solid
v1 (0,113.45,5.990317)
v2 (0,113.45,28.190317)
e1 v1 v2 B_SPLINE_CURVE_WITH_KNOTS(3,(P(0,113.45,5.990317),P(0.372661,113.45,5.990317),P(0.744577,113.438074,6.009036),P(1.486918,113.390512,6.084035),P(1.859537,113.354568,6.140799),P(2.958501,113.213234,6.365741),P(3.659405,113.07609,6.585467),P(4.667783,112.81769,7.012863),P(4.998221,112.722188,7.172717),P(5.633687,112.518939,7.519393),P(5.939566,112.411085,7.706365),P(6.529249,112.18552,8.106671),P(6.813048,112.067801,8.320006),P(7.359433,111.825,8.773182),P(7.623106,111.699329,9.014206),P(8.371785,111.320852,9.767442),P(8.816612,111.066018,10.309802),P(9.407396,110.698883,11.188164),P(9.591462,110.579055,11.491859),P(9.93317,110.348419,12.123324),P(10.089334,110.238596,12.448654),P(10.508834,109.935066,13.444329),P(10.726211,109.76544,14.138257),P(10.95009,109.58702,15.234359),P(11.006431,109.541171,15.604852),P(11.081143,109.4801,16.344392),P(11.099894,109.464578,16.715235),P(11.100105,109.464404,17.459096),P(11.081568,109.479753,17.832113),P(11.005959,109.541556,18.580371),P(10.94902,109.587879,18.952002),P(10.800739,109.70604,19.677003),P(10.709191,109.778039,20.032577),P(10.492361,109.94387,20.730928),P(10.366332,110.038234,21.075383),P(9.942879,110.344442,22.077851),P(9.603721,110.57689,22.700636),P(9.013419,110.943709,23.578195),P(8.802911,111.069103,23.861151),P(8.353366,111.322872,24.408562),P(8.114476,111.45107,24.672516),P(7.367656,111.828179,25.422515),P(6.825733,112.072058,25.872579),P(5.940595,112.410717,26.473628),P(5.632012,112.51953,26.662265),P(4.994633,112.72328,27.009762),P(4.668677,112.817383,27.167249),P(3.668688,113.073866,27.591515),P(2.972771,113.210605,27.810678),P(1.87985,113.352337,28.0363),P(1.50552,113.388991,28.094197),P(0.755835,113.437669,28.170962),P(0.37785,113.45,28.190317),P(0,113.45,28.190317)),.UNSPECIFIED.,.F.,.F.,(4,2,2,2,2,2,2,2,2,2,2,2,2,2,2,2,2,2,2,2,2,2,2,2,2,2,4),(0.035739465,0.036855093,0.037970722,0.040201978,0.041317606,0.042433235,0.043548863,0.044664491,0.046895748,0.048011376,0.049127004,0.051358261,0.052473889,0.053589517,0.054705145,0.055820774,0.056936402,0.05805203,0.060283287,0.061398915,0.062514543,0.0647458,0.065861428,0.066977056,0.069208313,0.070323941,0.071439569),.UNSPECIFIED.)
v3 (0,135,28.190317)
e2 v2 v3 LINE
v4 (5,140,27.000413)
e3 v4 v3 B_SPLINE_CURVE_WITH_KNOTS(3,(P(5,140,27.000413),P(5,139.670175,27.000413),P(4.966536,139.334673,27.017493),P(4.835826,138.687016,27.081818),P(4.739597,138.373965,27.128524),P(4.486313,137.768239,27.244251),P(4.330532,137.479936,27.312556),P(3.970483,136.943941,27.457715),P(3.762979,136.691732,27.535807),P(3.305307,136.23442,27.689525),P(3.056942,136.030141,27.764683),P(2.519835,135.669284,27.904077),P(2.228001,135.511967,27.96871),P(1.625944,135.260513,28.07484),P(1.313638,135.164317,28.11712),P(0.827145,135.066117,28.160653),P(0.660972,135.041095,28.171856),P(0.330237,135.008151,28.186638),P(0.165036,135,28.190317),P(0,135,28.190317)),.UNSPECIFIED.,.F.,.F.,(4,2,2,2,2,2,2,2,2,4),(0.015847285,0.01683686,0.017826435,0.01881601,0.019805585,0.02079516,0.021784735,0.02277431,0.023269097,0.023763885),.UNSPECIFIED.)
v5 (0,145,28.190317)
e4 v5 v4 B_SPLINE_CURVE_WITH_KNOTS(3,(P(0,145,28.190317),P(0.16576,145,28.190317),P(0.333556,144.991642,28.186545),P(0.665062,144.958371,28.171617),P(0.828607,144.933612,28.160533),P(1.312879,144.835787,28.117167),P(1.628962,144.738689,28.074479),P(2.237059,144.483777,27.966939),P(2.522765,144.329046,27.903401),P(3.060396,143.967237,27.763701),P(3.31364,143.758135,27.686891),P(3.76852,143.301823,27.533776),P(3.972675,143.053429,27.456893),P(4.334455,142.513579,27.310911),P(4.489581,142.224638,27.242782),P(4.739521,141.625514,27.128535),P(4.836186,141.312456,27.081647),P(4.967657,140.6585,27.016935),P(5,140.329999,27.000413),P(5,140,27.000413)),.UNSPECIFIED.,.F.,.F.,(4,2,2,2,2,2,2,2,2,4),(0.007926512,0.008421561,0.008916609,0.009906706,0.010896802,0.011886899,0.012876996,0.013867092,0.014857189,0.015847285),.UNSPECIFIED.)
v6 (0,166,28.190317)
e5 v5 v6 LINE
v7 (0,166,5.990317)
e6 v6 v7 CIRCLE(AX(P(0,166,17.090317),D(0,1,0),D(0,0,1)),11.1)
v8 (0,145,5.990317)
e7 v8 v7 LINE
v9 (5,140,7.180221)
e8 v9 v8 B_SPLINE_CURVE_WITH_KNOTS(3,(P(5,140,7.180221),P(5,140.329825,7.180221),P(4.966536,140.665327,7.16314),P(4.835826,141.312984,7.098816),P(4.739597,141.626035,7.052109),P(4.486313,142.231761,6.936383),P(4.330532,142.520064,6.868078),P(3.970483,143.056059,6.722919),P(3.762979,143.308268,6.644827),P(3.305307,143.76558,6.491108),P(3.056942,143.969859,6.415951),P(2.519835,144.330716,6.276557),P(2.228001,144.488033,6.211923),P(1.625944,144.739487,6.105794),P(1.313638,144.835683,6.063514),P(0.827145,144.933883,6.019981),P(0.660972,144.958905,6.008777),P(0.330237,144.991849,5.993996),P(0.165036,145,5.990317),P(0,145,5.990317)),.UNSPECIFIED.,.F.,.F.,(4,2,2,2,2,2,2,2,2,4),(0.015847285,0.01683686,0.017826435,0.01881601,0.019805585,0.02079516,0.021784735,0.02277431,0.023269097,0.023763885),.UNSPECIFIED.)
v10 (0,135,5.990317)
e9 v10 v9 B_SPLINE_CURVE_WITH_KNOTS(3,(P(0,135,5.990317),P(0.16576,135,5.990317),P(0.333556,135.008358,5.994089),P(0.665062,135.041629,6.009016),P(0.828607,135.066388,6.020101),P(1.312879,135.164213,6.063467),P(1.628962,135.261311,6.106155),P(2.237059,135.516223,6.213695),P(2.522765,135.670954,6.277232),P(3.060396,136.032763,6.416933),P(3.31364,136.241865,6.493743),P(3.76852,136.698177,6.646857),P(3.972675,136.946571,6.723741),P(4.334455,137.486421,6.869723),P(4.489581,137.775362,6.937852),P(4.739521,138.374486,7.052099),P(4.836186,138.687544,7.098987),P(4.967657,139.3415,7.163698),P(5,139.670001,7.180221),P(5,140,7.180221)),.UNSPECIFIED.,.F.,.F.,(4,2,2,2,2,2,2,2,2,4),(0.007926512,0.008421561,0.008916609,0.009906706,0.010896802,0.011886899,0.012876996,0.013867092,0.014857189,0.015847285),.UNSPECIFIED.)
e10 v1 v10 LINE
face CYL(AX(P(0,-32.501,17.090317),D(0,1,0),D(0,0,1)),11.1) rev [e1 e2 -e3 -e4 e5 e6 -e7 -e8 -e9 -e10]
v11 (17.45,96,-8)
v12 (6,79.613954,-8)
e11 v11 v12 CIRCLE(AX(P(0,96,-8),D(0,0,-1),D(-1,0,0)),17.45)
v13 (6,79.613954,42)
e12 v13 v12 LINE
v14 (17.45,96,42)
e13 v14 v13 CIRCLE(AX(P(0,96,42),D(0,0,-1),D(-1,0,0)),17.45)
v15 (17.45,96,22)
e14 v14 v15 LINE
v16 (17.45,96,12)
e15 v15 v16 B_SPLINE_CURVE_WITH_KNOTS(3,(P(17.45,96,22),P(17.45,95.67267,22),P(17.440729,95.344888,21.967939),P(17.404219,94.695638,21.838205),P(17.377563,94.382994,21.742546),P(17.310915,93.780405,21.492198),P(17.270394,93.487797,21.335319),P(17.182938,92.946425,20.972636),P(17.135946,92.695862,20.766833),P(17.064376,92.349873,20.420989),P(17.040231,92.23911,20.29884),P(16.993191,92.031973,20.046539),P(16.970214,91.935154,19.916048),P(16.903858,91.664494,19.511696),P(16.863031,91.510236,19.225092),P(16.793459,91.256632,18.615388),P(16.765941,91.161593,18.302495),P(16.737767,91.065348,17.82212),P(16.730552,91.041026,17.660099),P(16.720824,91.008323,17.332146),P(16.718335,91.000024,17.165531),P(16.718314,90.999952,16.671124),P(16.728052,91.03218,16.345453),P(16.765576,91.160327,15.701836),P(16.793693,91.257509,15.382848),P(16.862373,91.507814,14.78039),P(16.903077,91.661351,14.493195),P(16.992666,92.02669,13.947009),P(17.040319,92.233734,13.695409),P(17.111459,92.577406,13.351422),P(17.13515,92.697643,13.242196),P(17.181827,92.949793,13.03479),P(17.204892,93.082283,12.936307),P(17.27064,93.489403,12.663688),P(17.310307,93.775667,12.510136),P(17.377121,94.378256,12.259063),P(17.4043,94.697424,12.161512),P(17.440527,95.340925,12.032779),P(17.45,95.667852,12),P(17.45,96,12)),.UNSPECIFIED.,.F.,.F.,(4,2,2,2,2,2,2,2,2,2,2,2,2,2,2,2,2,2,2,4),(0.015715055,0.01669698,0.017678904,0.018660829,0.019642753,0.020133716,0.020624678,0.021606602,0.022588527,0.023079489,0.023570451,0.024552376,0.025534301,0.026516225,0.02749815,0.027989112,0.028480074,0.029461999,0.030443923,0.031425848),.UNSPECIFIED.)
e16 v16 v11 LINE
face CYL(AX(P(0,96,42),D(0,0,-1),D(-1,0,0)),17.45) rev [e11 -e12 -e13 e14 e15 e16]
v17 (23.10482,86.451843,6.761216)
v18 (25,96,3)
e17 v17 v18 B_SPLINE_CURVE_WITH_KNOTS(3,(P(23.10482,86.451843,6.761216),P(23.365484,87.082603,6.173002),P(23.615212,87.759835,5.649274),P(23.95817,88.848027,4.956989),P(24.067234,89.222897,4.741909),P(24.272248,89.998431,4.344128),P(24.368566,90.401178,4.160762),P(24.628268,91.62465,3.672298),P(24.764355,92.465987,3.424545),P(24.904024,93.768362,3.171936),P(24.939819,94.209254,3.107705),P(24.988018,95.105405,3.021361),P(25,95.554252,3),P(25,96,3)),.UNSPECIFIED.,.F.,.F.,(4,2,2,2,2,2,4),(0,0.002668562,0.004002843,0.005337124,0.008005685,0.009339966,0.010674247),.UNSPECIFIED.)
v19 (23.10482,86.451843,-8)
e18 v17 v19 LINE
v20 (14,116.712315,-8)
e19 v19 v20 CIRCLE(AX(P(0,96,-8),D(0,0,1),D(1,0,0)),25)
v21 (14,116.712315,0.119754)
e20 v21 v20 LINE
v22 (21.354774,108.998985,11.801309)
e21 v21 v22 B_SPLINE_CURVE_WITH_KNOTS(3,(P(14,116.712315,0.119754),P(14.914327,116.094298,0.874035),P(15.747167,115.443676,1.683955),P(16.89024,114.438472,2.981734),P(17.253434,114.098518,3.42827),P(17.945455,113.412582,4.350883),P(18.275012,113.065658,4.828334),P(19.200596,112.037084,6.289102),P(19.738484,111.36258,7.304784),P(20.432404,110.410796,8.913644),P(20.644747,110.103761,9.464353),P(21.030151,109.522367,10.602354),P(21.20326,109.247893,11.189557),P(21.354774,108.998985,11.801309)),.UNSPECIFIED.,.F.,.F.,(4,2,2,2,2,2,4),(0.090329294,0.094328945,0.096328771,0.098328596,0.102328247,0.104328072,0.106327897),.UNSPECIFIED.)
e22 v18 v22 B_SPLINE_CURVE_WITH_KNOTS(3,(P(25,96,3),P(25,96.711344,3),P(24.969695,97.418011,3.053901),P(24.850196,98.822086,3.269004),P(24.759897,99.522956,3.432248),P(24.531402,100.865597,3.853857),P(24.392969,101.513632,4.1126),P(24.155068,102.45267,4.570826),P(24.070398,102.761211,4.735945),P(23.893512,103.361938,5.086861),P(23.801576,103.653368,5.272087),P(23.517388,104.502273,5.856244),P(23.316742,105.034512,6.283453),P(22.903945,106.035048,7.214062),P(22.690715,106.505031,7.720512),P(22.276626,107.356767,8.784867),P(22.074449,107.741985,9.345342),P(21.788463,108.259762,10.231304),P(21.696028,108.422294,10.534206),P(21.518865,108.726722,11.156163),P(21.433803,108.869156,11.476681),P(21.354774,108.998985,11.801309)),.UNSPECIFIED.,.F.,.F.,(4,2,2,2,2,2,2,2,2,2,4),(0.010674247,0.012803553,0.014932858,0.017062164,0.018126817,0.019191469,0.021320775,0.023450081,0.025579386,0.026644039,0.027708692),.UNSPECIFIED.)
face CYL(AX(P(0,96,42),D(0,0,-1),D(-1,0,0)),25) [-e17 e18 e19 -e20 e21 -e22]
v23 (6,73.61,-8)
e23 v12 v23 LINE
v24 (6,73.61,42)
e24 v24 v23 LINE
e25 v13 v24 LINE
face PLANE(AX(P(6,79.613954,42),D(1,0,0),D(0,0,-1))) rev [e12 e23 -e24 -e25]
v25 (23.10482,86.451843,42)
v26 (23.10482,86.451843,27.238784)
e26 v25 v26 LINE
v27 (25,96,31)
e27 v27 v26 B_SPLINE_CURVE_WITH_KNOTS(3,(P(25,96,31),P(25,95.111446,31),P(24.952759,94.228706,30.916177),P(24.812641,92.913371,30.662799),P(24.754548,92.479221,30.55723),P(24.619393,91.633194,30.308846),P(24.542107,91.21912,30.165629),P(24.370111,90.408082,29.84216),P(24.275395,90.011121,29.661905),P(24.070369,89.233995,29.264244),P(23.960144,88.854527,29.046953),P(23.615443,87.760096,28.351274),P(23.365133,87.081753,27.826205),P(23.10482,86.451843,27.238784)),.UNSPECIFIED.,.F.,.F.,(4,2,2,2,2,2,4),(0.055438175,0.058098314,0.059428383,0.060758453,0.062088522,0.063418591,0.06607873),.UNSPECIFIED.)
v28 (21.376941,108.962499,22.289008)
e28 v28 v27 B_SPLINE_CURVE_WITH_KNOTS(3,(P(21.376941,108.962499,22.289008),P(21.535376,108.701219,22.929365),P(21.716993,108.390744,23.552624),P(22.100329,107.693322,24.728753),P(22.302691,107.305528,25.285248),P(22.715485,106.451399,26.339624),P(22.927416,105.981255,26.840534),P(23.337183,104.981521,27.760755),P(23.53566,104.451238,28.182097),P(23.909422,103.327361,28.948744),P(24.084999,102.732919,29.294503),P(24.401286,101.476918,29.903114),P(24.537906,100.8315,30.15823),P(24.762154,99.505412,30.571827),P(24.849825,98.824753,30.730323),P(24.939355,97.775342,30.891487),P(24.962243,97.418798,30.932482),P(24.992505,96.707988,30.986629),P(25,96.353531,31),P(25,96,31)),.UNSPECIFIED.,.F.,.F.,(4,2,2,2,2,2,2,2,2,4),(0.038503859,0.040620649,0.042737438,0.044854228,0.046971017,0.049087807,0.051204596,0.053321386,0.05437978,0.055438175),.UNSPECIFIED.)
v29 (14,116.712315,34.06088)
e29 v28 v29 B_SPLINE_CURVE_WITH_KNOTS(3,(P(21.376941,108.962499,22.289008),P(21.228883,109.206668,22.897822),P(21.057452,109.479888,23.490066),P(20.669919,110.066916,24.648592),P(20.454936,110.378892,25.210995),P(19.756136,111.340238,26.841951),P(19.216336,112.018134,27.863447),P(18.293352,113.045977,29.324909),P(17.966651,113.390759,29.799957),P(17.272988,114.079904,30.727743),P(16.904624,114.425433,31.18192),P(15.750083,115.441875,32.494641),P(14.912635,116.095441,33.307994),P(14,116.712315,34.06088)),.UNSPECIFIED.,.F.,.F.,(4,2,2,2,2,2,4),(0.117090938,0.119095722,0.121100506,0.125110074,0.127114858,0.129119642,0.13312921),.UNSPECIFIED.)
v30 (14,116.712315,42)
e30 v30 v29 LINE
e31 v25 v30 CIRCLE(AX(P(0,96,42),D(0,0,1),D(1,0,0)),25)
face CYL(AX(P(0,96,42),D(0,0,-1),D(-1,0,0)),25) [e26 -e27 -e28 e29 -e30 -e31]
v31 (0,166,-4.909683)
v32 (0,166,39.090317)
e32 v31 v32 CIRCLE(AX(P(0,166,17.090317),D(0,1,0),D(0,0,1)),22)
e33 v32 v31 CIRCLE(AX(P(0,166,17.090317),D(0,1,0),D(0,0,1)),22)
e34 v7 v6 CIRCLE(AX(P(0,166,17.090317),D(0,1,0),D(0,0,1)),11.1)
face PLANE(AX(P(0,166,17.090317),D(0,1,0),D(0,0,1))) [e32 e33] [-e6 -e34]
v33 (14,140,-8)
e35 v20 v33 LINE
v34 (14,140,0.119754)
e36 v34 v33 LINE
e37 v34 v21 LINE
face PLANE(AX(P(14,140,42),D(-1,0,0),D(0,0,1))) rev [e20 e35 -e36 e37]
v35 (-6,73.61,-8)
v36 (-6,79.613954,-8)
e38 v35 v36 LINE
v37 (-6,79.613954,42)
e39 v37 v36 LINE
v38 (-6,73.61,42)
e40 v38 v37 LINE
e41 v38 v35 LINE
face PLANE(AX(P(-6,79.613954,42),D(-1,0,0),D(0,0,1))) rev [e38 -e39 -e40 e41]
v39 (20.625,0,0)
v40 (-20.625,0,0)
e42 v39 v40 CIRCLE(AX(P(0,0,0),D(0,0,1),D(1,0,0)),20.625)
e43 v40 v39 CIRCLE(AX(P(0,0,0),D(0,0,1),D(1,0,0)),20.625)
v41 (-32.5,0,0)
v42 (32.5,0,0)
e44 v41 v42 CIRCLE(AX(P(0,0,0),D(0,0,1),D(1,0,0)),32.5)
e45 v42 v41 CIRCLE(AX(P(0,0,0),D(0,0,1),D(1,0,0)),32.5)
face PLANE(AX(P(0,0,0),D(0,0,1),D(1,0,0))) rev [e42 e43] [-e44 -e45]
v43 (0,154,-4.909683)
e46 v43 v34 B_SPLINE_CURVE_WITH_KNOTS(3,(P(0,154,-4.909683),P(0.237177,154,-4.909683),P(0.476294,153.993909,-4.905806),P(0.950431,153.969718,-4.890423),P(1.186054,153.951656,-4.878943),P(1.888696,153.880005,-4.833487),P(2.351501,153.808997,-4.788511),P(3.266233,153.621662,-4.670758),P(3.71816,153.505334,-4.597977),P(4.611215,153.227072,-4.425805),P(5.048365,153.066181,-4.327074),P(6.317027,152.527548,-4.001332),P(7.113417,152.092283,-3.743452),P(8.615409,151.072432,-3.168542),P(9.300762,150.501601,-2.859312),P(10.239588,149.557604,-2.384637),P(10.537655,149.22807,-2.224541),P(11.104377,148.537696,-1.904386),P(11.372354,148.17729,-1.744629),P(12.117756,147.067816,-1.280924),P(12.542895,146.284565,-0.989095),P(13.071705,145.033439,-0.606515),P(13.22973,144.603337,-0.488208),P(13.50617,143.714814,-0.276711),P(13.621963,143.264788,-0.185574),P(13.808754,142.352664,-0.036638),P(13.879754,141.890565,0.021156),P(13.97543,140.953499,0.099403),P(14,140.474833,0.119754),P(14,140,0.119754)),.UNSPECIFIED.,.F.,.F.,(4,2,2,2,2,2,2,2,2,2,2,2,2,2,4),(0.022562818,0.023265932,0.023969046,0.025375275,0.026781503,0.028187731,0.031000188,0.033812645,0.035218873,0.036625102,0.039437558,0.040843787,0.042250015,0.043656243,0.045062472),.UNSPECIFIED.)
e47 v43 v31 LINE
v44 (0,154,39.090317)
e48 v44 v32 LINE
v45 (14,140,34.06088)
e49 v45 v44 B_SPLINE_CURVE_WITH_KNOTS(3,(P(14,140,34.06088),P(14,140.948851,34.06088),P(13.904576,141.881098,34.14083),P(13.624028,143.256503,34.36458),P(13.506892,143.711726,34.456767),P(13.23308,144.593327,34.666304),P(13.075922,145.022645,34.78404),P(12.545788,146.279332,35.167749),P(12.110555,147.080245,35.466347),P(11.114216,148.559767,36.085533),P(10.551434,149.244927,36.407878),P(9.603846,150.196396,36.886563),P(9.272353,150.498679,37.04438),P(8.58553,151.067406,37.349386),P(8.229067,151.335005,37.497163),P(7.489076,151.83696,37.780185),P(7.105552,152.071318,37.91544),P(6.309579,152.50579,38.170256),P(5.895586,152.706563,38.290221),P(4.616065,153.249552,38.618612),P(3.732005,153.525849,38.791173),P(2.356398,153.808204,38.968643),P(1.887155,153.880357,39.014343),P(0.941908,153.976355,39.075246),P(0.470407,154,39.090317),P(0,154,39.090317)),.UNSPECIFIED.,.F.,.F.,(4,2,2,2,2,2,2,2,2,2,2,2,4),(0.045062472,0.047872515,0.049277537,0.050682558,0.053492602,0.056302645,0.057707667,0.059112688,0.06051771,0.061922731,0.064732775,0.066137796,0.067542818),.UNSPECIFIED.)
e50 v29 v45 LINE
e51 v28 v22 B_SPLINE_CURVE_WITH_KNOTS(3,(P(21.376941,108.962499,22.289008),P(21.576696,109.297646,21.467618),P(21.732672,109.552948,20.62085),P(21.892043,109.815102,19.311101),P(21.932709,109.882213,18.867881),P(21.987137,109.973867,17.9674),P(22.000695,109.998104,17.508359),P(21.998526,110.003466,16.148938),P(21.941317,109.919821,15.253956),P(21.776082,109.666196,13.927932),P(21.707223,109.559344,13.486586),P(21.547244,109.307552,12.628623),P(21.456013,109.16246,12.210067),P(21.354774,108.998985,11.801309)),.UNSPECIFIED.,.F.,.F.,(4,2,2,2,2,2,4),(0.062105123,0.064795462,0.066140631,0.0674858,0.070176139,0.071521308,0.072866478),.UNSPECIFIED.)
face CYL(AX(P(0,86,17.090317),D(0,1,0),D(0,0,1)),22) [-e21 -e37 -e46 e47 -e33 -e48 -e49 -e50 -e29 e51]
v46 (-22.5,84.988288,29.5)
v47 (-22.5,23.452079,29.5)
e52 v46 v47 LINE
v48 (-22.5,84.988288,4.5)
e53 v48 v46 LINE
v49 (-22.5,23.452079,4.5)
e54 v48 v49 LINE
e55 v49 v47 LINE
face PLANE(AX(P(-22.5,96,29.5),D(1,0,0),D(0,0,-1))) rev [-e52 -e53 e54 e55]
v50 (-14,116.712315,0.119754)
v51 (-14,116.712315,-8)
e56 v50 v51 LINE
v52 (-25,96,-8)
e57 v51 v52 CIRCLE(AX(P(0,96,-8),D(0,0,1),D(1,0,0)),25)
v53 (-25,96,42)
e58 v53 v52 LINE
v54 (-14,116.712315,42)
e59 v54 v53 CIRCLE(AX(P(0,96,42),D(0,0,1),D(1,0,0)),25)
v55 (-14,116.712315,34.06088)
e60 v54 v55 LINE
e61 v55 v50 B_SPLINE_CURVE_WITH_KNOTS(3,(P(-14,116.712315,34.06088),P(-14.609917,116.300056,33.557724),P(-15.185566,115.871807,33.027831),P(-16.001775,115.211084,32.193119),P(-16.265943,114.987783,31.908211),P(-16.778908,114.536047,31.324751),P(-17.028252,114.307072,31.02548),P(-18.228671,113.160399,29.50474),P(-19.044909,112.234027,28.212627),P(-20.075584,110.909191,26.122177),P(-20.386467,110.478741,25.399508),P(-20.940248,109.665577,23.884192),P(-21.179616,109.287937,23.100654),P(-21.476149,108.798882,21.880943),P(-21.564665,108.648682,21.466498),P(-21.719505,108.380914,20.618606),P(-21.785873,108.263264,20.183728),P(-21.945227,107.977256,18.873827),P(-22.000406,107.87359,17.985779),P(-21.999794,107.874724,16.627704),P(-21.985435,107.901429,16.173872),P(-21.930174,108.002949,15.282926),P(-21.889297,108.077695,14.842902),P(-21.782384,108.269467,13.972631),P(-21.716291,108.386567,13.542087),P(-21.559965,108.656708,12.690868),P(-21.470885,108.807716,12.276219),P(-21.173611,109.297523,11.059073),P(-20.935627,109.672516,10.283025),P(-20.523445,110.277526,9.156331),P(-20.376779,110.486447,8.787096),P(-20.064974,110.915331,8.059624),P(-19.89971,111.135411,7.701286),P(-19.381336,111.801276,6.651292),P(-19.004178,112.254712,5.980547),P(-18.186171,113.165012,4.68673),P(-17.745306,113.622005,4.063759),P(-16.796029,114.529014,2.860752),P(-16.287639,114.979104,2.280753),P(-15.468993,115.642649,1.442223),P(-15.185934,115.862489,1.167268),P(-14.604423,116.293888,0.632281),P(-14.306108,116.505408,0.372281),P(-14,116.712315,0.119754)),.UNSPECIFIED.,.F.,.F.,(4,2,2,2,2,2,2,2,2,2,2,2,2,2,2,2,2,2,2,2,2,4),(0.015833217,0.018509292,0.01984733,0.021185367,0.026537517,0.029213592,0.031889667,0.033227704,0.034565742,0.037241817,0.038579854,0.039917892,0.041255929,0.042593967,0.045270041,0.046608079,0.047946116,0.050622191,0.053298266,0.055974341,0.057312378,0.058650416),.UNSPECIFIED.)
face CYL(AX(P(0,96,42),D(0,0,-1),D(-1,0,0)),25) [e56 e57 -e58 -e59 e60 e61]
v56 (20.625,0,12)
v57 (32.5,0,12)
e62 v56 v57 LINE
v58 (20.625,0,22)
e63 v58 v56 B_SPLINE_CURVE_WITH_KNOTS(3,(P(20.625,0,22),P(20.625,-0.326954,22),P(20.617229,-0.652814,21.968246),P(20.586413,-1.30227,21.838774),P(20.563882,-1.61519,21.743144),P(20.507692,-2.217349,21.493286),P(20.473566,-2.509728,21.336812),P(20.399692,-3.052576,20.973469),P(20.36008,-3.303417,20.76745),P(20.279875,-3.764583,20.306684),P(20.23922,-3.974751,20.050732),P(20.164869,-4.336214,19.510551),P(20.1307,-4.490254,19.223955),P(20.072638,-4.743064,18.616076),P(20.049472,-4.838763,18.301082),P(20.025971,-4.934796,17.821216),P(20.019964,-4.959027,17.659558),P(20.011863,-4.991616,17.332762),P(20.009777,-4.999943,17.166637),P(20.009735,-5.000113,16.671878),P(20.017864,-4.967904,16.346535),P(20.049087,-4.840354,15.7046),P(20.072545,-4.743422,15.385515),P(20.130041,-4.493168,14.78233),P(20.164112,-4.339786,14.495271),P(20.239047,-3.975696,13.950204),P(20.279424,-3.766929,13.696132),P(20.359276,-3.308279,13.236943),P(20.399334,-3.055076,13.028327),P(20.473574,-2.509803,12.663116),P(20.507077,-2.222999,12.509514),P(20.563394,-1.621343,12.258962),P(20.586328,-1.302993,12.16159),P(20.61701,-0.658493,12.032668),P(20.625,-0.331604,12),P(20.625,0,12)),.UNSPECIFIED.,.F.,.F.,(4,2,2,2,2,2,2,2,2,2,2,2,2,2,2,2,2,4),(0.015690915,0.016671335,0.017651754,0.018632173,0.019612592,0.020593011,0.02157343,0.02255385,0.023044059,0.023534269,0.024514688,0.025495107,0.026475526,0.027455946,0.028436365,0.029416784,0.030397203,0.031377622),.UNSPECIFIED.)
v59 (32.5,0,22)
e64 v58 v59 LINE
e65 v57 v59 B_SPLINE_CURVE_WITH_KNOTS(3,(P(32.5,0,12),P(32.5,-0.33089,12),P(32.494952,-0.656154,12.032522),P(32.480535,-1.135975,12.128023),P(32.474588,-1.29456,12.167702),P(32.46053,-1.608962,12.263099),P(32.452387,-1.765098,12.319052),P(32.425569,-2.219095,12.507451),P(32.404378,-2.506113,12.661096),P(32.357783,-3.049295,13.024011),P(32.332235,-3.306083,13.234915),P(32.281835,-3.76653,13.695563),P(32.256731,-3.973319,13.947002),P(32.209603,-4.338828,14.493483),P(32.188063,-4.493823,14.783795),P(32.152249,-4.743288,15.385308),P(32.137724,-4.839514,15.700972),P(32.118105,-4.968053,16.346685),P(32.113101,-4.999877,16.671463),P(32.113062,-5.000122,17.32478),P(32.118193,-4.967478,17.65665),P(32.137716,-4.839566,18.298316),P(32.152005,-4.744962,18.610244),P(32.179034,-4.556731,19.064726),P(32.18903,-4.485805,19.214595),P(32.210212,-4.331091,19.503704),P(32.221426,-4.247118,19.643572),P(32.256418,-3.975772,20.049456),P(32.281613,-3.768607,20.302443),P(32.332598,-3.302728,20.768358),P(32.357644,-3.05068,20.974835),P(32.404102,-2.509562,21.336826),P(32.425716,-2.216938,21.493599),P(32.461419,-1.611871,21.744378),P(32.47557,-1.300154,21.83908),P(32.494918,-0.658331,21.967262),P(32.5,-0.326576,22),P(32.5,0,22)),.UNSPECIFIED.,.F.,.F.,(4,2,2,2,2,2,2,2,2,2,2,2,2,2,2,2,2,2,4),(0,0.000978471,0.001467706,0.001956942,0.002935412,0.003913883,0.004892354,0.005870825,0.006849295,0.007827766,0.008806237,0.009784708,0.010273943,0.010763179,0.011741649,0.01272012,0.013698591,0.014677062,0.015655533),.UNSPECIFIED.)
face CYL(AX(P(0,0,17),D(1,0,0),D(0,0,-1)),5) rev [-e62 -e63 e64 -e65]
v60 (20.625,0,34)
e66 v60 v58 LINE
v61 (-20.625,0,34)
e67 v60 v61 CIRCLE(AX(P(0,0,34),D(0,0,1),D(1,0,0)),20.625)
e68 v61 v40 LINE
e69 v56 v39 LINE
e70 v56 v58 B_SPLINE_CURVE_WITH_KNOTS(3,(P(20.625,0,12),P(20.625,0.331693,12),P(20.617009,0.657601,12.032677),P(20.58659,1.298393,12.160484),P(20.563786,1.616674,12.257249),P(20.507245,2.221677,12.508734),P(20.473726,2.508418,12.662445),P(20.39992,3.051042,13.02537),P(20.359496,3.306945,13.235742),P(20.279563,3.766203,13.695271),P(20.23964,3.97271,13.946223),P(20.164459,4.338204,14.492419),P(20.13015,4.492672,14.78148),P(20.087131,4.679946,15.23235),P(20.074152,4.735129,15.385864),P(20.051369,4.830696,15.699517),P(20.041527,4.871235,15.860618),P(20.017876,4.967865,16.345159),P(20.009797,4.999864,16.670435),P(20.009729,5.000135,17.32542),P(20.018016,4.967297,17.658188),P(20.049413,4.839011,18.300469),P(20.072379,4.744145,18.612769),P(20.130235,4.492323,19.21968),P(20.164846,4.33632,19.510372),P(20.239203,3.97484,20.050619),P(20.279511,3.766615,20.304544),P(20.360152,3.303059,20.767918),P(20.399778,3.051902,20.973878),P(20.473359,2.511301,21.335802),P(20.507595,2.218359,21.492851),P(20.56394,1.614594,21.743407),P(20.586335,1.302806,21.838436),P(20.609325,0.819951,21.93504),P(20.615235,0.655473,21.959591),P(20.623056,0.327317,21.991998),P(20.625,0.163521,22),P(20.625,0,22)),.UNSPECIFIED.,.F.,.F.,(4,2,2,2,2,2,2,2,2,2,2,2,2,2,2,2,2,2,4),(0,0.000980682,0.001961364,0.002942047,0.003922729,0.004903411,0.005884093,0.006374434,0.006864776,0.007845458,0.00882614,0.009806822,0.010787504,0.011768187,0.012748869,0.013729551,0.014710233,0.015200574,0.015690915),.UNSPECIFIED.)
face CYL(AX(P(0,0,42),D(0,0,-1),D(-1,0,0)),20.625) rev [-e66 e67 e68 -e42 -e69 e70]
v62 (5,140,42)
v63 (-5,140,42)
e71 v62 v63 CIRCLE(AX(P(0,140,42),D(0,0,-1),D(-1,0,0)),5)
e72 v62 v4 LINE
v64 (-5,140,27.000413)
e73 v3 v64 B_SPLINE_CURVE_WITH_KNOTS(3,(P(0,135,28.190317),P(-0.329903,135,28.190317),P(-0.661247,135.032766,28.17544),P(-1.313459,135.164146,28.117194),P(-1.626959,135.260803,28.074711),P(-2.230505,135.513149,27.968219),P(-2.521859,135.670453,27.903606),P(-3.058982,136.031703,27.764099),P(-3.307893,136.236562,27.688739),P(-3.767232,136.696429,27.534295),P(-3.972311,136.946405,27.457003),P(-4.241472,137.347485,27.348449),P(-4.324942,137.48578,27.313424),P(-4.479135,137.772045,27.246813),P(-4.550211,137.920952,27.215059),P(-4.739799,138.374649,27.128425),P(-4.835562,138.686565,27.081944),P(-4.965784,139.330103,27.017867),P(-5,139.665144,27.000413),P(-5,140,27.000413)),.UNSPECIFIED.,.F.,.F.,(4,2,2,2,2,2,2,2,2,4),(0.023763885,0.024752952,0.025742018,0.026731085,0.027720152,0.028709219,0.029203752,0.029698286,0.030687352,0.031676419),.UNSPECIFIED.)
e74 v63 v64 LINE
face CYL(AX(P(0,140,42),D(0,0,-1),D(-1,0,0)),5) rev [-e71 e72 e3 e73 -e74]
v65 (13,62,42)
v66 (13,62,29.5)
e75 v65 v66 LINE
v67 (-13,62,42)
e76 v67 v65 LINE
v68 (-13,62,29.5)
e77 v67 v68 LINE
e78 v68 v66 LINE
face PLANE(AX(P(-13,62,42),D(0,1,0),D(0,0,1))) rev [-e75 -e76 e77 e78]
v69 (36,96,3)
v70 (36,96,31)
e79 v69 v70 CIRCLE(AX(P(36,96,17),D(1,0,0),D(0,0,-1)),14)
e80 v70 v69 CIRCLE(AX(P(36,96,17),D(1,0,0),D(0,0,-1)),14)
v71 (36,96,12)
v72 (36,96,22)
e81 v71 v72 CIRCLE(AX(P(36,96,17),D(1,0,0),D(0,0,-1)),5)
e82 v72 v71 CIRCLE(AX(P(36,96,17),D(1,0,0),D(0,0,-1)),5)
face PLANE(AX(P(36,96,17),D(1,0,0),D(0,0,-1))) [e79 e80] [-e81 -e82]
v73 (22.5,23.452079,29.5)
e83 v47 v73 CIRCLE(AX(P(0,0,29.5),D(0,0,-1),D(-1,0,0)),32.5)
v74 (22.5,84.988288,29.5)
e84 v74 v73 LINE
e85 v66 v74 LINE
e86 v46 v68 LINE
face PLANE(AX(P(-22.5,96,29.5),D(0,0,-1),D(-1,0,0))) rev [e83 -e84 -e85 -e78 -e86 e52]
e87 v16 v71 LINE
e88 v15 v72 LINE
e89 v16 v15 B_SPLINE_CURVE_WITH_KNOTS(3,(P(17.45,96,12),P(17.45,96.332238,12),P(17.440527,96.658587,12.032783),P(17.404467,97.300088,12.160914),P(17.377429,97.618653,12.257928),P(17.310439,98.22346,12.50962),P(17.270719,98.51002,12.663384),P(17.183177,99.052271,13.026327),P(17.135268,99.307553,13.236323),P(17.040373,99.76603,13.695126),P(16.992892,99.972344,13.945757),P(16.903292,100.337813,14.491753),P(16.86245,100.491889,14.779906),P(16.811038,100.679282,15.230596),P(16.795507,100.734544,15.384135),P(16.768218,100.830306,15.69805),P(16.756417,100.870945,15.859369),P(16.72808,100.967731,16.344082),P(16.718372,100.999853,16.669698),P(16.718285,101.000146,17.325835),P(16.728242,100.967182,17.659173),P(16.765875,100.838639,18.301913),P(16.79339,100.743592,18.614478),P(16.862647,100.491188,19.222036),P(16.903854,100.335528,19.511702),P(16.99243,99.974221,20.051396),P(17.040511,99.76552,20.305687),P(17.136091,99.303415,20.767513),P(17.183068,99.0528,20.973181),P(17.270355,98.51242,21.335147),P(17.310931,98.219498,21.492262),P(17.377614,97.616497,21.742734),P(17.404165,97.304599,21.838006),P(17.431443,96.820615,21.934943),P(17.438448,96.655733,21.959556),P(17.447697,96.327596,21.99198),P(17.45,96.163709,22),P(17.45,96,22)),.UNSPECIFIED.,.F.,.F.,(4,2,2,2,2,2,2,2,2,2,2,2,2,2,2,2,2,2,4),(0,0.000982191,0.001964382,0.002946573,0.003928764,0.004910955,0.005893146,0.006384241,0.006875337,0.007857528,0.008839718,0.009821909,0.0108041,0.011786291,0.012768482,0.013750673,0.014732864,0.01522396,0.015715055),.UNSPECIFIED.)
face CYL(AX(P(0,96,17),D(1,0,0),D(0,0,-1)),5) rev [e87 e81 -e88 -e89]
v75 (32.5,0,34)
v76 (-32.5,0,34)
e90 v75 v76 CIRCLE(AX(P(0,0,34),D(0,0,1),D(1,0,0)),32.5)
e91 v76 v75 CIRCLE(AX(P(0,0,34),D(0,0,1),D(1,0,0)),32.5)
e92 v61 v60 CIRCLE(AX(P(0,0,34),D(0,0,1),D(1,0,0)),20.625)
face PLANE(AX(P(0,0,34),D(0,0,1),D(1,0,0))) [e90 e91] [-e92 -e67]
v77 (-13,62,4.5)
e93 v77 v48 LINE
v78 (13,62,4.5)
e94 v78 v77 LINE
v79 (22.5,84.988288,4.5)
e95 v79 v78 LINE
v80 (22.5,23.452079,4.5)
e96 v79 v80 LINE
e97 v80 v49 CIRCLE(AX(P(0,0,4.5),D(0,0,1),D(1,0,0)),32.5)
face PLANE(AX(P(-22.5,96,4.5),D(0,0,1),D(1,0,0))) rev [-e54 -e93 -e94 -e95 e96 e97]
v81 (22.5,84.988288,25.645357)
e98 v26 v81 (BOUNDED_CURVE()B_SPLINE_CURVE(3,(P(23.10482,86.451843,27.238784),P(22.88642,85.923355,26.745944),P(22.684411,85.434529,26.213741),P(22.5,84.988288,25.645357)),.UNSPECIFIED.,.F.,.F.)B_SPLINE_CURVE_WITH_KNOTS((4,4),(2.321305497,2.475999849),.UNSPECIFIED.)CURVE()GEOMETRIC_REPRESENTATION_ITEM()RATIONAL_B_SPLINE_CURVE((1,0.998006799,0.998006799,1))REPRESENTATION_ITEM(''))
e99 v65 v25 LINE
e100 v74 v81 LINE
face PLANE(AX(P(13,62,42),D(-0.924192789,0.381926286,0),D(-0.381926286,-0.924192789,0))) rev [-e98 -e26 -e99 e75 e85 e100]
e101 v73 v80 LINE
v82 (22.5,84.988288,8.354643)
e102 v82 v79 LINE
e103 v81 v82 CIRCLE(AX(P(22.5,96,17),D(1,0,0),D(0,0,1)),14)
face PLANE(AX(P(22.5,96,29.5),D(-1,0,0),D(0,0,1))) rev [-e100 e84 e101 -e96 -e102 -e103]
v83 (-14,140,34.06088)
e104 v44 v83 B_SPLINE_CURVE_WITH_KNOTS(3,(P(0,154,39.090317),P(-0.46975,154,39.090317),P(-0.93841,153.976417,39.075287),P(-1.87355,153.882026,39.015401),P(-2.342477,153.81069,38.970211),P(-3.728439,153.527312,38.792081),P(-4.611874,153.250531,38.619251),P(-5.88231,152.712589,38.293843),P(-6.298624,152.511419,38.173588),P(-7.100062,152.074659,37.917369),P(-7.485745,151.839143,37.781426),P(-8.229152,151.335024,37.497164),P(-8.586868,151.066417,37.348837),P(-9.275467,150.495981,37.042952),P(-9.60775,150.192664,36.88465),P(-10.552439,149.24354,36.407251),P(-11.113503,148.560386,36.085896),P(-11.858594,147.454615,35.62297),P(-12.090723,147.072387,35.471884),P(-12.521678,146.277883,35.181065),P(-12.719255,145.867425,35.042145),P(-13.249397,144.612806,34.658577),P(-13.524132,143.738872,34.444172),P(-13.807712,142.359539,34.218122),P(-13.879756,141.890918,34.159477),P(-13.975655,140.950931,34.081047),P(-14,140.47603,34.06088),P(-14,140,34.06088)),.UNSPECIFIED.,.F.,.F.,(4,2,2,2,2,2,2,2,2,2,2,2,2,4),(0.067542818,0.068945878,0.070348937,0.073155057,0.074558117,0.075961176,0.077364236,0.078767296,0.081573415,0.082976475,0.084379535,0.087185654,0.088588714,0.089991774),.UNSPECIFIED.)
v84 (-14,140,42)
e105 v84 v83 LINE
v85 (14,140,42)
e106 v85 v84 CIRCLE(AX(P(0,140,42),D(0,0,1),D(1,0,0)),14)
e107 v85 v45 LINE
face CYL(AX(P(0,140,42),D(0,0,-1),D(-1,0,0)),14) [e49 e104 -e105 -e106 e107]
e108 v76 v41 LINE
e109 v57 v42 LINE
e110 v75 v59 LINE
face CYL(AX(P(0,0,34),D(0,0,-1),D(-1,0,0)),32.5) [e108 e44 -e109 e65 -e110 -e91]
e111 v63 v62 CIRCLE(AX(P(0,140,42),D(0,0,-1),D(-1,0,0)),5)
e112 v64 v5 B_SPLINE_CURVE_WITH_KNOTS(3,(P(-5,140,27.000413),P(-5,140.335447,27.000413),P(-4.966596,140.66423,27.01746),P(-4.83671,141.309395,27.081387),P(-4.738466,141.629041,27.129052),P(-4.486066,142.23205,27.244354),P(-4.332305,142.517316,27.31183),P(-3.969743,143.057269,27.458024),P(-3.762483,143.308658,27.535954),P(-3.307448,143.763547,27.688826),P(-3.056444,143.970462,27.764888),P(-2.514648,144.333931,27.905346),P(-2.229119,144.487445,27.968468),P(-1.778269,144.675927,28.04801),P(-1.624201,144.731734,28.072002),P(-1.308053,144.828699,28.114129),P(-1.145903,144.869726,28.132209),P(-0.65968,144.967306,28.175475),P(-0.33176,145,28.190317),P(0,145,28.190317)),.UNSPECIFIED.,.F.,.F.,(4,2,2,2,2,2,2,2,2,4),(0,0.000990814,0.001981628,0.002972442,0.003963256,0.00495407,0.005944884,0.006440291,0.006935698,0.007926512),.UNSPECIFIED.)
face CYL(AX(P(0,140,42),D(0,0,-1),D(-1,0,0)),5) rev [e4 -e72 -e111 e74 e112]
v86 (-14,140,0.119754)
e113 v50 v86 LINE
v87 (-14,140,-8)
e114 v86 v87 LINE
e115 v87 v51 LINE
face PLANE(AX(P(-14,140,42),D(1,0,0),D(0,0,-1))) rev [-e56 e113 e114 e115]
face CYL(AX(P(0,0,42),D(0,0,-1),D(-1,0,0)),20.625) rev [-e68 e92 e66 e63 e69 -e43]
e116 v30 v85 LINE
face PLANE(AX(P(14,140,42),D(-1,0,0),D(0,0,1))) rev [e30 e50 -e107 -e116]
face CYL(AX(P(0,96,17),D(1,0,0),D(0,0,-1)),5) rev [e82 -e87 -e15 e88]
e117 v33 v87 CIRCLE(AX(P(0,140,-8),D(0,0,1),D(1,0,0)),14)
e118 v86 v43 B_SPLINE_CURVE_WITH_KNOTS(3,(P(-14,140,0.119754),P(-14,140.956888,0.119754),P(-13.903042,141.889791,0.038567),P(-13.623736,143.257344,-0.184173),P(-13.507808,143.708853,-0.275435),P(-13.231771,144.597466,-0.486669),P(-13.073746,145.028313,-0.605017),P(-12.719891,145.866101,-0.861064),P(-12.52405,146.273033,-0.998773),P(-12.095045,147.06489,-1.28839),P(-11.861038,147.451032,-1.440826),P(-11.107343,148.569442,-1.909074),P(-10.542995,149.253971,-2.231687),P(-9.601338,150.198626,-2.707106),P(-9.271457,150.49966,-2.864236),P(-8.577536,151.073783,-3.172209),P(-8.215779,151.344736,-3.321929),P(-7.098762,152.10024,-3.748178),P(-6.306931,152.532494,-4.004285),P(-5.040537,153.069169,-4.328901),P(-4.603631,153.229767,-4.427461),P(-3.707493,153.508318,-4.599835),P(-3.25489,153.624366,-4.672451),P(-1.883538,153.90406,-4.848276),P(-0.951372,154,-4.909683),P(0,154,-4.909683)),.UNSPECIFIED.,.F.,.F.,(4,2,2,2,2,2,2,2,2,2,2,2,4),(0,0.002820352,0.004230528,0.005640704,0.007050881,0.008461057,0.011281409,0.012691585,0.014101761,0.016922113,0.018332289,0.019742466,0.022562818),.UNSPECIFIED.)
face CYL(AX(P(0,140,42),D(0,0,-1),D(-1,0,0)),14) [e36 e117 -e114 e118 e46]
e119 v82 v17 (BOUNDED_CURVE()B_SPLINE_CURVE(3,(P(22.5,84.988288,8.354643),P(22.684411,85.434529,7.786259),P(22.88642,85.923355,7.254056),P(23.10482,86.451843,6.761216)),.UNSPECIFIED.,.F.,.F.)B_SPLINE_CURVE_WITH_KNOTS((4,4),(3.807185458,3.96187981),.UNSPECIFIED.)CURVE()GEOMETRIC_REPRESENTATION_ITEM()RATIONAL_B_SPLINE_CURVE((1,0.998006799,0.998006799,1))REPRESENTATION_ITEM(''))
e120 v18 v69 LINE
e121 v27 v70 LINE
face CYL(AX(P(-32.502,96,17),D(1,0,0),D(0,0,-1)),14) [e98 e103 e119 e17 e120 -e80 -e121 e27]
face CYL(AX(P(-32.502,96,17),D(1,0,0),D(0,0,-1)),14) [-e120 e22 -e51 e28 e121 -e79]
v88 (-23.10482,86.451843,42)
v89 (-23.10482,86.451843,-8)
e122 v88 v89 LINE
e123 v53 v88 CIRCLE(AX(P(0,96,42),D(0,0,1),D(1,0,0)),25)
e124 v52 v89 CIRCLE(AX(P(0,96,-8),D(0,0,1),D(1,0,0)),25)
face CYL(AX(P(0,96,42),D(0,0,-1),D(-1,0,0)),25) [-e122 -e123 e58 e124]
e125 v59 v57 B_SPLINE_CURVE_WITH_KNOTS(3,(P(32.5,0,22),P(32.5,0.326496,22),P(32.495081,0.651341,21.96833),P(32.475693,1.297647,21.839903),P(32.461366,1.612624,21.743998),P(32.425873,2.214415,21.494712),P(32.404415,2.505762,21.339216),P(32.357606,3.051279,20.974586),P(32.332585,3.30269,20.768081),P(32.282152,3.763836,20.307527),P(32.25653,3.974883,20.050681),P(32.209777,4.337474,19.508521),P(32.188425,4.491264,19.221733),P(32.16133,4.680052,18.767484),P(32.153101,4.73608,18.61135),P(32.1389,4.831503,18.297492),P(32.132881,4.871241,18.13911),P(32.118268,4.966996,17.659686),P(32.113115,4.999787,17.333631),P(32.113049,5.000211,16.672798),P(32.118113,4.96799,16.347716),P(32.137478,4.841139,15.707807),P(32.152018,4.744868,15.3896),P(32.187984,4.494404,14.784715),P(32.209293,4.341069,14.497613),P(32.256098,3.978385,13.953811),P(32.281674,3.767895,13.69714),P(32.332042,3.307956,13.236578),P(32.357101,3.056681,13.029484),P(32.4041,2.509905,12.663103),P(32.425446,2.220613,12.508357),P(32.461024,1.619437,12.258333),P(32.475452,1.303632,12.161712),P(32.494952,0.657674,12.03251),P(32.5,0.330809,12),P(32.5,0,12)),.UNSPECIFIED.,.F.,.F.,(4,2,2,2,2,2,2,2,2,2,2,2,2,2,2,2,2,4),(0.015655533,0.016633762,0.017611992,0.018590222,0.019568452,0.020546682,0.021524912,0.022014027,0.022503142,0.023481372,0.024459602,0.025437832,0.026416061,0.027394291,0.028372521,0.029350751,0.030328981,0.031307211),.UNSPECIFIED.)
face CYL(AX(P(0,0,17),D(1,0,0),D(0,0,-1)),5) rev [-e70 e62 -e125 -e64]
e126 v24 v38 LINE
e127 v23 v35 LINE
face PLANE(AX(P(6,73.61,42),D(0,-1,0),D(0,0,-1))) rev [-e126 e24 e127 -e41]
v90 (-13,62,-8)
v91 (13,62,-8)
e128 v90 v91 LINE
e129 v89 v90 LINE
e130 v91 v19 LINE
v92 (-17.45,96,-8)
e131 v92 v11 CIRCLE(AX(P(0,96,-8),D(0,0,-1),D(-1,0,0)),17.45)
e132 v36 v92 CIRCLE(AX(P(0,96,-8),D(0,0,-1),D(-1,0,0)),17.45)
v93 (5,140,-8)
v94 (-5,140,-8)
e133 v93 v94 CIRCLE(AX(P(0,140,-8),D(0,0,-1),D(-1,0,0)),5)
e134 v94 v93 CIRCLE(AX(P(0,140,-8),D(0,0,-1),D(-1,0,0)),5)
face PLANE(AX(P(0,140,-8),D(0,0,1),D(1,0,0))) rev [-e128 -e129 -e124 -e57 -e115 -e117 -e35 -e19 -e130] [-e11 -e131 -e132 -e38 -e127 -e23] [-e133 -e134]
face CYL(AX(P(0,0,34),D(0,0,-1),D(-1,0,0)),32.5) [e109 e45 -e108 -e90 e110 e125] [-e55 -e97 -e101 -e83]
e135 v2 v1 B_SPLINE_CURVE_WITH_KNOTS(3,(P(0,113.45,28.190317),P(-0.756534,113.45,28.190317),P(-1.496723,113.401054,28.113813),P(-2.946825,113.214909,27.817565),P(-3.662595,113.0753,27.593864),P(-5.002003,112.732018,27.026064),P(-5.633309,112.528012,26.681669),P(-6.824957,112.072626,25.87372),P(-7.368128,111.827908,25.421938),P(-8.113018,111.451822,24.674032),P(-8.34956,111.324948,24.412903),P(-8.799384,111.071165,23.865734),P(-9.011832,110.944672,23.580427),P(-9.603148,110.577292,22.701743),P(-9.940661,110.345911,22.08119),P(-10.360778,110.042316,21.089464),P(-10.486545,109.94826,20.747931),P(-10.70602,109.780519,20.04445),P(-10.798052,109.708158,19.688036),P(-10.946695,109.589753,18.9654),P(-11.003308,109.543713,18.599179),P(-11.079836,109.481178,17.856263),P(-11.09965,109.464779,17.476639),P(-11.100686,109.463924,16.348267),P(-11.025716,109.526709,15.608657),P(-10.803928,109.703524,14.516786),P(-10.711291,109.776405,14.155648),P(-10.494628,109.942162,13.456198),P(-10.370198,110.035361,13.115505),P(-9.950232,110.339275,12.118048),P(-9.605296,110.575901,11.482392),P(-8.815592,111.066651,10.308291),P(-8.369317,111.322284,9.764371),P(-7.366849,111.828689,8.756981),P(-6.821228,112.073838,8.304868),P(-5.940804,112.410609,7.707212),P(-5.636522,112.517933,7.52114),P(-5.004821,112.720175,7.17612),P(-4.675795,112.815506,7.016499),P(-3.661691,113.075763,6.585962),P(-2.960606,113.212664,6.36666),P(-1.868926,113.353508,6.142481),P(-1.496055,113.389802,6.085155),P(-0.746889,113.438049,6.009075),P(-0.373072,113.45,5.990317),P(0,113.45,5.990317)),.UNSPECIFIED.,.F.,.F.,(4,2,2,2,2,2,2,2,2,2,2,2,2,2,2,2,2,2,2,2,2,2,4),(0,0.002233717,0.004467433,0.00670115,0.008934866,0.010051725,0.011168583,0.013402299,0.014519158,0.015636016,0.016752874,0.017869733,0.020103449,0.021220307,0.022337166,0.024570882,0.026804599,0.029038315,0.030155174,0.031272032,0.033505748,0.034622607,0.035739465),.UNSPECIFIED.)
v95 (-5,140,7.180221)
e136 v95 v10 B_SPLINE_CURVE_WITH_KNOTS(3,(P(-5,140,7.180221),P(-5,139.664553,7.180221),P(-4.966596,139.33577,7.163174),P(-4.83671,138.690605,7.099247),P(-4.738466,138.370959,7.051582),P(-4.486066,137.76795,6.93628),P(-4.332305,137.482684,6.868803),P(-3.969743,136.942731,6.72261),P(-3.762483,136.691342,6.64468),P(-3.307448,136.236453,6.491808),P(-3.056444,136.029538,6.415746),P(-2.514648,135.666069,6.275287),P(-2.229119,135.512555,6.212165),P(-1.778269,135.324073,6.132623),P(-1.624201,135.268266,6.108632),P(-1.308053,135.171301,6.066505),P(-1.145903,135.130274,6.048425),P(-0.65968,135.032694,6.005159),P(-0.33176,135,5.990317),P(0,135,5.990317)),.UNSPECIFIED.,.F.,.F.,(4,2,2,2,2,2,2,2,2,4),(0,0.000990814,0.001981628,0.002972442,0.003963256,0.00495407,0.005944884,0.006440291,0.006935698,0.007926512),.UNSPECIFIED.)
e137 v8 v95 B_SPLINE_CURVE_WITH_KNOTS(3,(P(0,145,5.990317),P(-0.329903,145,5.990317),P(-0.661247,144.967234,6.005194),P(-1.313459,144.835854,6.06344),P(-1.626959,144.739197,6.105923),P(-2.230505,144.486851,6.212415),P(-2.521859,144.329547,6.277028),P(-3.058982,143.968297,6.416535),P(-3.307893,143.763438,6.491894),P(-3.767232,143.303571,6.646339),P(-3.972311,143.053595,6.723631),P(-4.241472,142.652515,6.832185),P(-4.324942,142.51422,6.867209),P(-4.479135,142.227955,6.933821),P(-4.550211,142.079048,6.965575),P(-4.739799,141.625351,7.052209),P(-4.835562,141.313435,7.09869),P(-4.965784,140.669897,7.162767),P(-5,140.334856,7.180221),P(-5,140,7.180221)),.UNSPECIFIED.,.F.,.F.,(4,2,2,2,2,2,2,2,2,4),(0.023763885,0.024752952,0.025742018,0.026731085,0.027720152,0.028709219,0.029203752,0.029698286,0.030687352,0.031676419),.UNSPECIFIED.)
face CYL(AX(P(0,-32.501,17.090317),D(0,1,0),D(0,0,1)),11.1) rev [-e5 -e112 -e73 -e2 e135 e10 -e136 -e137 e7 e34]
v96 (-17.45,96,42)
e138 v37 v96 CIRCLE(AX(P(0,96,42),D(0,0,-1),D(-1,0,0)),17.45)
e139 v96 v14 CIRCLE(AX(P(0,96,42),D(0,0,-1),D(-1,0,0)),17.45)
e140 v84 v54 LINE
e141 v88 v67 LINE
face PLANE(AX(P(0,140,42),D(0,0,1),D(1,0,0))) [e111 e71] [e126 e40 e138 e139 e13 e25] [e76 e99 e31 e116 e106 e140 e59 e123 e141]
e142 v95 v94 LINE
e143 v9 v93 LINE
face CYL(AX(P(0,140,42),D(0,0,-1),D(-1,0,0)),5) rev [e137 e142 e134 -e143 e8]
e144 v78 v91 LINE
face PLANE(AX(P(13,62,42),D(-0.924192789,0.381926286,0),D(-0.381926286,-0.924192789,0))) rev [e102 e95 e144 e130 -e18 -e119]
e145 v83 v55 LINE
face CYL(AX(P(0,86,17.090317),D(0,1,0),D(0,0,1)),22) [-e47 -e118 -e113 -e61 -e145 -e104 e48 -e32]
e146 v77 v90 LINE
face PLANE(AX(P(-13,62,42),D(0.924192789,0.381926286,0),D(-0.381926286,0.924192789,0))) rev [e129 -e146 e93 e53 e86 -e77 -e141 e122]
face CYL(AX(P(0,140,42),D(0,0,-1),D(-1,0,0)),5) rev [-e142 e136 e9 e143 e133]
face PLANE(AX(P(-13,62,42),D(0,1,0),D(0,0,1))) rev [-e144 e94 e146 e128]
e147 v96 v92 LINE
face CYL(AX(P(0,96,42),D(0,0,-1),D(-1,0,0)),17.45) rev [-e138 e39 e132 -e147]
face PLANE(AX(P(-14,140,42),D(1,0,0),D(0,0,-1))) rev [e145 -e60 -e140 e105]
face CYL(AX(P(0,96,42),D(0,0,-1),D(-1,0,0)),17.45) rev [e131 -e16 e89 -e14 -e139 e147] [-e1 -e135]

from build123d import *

# Parameters (mm, degrees)
BIG_END_EYE_SKETCH_R     = 32.5
BIG_END_EYE_65_DEPTH     = 34
ROD_SHANK_SKETCH_W       = 45
ROD_SHANK_SKETCH_H       = 25
ROD_SHANK_DEPTH          = 96
SMALL_START              = 17
SMALL_END_CLEVIS_DEPTH   = 25
TOP_START                = 166
TOP_BOSS_SKETCH_R        = 22
TOP_BOSS_44_DEPTH        = 80
KEYED_BORE_SKETCH_R      = 20.625
KEYED_BORE_SKETCH_R_2    = 5
KEYED_BORE_CUT_DEPTH     = 177.386649277
SIDE_START               = 21.354774
SIDE_BOSS_SKETCH_R       = 14
SIDE_BOSS_28_DEPTH       = 14.645226
SIDE_PIN_HOLE_SKETCH_R   = 5
SIDE_PIN_HOLE_10_DEPTH   = 36
TOP_BORE_22_2_REACH      = 208.064
TOP_BORE_22_2_END_RADIUS = 17.45
TOP_BORE_SKETCH_R        = 11.1


with BuildPart() as part:
    # Big End Eye Sketch → Big End Eye Ø65 (new body)
    with BuildSketch(Plane.XY):
        Circle(BIG_END_EYE_SKETCH_R)
    extrude(amount=BIG_END_EYE_65_DEPTH)

    # Rod Shank Sketch → Rod Shank (add)
    with BuildSketch(Plane(origin=(0, 0, 0), x_dir=(1, 0, 0), z_dir=(0, 1, 0))):
        with Locations((0, -17)):
            Rectangle(ROD_SHANK_SKETCH_W, ROD_SHANK_SKETCH_H)
    extrude(amount=ROD_SHANK_DEPTH)

    # Small End Clevis Sketch → Small End Clevis (add, symmetric)
    with BuildSketch(Plane.XY.offset(SMALL_START)):
        with BuildLine():
            Line((-14, 140), (-14, 116.712315177))
            ThreePointArc((-14, 116.712315177), (-23.9398404, 103.203057798), (-23.104819731, 86.451842838))
            Line((-23.104819731, 86.451842838), (-13, 62))
            Line((-13, 62), (13, 62))
            Line((13, 62), (23.104819731, 86.451842838))
            ThreePointArc((23.104819731, 86.451842838), (23.9398404, 103.203057798), (14, 116.712315177))
            Line((14, 116.712315177), (14, 140))
            ThreePointArc((14, 140), (0, 154), (-14, 140))
        make_face()
    extrude(amount=SMALL_END_CLEVIS_DEPTH, both=True)

    # Top Boss Sketch → Top Boss Ø44 (add)
    with BuildSketch(Plane(origin=(0, 0, 0), x_dir=(1, 0, 0), z_dir=(0, 1, 0)).offset(TOP_START)):
        with Locations(Location((0, -17.090316824, 0), (0, 0, 270))):
            Circle(TOP_BOSS_SKETCH_R)
    extrude(amount=-TOP_BOSS_44_DEPTH)

    # Keyed Bore Sketch → Keyed Bore Cut (cut, through all)
    with BuildSketch(Plane(origin=(0, 0, -8), x_dir=(-1, 0, 0), z_dir=(0, 0, -1))):
        with Locations(Location((0, 0, 0), (0, 0, 180))):
            Circle(KEYED_BORE_SKETCH_R)
        with Locations((0, 140)):
            Circle(KEYED_BORE_SKETCH_R_2)
        with BuildLine():
            Line((-6, 79.613954107), (-6, 73.61))
            Line((-6, 73.61), (6, 73.61))
            Line((6, 73.61), (6, 79.613954107))
            ThreePointArc((6, 79.613954107), (0, 113.45), (-6, 79.613954107))
        make_face()
    extrude(amount=-KEYED_BORE_CUT_DEPTH, mode=Mode.SUBTRACT)

    # Side Boss Sketch → Side Boss Ø28 (add)
    with BuildSketch(Plane(origin=(0, 0, 0), x_dir=(0, 0, -1), z_dir=(1, 0, 0)).offset(SIDE_START)):
        with Locations((-17, 96)):
            Circle(SIDE_BOSS_SKETCH_R)
    extrude(amount=SIDE_BOSS_28_DEPTH)

    # Side Pin Hole Sketch → Side Pin Hole Ø10 (cut)
    with BuildSketch(Plane(origin=(36, 0, 0), x_dir=(0, 0, -1), z_dir=(1, 0, 0))):
        with Locations((-17, 96)):
            Circle(SIDE_PIN_HOLE_SKETCH_R)
        with Locations((-17, 0)):
            Circle(SIDE_PIN_HOLE_SKETCH_R)
    extrude(amount=-SIDE_PIN_HOLE_10_DEPTH, mode=Mode.SUBTRACT)

    # Top Bore Ø22.2: up to this cylinder (the profile starts outside it)
    top_bore_22_2_end = Plane(origin=(0, 96, 17.090317), z_dir=(0, 0, -1)) * Cylinder(TOP_BORE_22_2_END_RADIUS, 452.028, mode=Mode.PRIVATE)
    # Top Bore Sketch → Top Bore Ø22.2 (cut, up to the surface)
    with BuildSketch(Plane(origin=(0, 166, 0), x_dir=(1, 0, 0), z_dir=(0, 1, 0)), mode=Mode.PRIVATE) as top_bore_22_2_sk1:
        with Locations(Location((0, -17.090316824, 0), (0, 0, 270))):
            Circle(TOP_BORE_SKETCH_R)
    top_bore_22_2_tool1 = extrude(top_bore_22_2_sk1.sketch, amount=-TOP_BORE_22_2_REACH, mode=Mode.PRIVATE) - top_bore_22_2_end
    add(top_bore_22_2_tool1.solids().sort_by_distance((0, 166, 17.090317))[0], mode=Mode.SUBTRACT)


solid = part.part
